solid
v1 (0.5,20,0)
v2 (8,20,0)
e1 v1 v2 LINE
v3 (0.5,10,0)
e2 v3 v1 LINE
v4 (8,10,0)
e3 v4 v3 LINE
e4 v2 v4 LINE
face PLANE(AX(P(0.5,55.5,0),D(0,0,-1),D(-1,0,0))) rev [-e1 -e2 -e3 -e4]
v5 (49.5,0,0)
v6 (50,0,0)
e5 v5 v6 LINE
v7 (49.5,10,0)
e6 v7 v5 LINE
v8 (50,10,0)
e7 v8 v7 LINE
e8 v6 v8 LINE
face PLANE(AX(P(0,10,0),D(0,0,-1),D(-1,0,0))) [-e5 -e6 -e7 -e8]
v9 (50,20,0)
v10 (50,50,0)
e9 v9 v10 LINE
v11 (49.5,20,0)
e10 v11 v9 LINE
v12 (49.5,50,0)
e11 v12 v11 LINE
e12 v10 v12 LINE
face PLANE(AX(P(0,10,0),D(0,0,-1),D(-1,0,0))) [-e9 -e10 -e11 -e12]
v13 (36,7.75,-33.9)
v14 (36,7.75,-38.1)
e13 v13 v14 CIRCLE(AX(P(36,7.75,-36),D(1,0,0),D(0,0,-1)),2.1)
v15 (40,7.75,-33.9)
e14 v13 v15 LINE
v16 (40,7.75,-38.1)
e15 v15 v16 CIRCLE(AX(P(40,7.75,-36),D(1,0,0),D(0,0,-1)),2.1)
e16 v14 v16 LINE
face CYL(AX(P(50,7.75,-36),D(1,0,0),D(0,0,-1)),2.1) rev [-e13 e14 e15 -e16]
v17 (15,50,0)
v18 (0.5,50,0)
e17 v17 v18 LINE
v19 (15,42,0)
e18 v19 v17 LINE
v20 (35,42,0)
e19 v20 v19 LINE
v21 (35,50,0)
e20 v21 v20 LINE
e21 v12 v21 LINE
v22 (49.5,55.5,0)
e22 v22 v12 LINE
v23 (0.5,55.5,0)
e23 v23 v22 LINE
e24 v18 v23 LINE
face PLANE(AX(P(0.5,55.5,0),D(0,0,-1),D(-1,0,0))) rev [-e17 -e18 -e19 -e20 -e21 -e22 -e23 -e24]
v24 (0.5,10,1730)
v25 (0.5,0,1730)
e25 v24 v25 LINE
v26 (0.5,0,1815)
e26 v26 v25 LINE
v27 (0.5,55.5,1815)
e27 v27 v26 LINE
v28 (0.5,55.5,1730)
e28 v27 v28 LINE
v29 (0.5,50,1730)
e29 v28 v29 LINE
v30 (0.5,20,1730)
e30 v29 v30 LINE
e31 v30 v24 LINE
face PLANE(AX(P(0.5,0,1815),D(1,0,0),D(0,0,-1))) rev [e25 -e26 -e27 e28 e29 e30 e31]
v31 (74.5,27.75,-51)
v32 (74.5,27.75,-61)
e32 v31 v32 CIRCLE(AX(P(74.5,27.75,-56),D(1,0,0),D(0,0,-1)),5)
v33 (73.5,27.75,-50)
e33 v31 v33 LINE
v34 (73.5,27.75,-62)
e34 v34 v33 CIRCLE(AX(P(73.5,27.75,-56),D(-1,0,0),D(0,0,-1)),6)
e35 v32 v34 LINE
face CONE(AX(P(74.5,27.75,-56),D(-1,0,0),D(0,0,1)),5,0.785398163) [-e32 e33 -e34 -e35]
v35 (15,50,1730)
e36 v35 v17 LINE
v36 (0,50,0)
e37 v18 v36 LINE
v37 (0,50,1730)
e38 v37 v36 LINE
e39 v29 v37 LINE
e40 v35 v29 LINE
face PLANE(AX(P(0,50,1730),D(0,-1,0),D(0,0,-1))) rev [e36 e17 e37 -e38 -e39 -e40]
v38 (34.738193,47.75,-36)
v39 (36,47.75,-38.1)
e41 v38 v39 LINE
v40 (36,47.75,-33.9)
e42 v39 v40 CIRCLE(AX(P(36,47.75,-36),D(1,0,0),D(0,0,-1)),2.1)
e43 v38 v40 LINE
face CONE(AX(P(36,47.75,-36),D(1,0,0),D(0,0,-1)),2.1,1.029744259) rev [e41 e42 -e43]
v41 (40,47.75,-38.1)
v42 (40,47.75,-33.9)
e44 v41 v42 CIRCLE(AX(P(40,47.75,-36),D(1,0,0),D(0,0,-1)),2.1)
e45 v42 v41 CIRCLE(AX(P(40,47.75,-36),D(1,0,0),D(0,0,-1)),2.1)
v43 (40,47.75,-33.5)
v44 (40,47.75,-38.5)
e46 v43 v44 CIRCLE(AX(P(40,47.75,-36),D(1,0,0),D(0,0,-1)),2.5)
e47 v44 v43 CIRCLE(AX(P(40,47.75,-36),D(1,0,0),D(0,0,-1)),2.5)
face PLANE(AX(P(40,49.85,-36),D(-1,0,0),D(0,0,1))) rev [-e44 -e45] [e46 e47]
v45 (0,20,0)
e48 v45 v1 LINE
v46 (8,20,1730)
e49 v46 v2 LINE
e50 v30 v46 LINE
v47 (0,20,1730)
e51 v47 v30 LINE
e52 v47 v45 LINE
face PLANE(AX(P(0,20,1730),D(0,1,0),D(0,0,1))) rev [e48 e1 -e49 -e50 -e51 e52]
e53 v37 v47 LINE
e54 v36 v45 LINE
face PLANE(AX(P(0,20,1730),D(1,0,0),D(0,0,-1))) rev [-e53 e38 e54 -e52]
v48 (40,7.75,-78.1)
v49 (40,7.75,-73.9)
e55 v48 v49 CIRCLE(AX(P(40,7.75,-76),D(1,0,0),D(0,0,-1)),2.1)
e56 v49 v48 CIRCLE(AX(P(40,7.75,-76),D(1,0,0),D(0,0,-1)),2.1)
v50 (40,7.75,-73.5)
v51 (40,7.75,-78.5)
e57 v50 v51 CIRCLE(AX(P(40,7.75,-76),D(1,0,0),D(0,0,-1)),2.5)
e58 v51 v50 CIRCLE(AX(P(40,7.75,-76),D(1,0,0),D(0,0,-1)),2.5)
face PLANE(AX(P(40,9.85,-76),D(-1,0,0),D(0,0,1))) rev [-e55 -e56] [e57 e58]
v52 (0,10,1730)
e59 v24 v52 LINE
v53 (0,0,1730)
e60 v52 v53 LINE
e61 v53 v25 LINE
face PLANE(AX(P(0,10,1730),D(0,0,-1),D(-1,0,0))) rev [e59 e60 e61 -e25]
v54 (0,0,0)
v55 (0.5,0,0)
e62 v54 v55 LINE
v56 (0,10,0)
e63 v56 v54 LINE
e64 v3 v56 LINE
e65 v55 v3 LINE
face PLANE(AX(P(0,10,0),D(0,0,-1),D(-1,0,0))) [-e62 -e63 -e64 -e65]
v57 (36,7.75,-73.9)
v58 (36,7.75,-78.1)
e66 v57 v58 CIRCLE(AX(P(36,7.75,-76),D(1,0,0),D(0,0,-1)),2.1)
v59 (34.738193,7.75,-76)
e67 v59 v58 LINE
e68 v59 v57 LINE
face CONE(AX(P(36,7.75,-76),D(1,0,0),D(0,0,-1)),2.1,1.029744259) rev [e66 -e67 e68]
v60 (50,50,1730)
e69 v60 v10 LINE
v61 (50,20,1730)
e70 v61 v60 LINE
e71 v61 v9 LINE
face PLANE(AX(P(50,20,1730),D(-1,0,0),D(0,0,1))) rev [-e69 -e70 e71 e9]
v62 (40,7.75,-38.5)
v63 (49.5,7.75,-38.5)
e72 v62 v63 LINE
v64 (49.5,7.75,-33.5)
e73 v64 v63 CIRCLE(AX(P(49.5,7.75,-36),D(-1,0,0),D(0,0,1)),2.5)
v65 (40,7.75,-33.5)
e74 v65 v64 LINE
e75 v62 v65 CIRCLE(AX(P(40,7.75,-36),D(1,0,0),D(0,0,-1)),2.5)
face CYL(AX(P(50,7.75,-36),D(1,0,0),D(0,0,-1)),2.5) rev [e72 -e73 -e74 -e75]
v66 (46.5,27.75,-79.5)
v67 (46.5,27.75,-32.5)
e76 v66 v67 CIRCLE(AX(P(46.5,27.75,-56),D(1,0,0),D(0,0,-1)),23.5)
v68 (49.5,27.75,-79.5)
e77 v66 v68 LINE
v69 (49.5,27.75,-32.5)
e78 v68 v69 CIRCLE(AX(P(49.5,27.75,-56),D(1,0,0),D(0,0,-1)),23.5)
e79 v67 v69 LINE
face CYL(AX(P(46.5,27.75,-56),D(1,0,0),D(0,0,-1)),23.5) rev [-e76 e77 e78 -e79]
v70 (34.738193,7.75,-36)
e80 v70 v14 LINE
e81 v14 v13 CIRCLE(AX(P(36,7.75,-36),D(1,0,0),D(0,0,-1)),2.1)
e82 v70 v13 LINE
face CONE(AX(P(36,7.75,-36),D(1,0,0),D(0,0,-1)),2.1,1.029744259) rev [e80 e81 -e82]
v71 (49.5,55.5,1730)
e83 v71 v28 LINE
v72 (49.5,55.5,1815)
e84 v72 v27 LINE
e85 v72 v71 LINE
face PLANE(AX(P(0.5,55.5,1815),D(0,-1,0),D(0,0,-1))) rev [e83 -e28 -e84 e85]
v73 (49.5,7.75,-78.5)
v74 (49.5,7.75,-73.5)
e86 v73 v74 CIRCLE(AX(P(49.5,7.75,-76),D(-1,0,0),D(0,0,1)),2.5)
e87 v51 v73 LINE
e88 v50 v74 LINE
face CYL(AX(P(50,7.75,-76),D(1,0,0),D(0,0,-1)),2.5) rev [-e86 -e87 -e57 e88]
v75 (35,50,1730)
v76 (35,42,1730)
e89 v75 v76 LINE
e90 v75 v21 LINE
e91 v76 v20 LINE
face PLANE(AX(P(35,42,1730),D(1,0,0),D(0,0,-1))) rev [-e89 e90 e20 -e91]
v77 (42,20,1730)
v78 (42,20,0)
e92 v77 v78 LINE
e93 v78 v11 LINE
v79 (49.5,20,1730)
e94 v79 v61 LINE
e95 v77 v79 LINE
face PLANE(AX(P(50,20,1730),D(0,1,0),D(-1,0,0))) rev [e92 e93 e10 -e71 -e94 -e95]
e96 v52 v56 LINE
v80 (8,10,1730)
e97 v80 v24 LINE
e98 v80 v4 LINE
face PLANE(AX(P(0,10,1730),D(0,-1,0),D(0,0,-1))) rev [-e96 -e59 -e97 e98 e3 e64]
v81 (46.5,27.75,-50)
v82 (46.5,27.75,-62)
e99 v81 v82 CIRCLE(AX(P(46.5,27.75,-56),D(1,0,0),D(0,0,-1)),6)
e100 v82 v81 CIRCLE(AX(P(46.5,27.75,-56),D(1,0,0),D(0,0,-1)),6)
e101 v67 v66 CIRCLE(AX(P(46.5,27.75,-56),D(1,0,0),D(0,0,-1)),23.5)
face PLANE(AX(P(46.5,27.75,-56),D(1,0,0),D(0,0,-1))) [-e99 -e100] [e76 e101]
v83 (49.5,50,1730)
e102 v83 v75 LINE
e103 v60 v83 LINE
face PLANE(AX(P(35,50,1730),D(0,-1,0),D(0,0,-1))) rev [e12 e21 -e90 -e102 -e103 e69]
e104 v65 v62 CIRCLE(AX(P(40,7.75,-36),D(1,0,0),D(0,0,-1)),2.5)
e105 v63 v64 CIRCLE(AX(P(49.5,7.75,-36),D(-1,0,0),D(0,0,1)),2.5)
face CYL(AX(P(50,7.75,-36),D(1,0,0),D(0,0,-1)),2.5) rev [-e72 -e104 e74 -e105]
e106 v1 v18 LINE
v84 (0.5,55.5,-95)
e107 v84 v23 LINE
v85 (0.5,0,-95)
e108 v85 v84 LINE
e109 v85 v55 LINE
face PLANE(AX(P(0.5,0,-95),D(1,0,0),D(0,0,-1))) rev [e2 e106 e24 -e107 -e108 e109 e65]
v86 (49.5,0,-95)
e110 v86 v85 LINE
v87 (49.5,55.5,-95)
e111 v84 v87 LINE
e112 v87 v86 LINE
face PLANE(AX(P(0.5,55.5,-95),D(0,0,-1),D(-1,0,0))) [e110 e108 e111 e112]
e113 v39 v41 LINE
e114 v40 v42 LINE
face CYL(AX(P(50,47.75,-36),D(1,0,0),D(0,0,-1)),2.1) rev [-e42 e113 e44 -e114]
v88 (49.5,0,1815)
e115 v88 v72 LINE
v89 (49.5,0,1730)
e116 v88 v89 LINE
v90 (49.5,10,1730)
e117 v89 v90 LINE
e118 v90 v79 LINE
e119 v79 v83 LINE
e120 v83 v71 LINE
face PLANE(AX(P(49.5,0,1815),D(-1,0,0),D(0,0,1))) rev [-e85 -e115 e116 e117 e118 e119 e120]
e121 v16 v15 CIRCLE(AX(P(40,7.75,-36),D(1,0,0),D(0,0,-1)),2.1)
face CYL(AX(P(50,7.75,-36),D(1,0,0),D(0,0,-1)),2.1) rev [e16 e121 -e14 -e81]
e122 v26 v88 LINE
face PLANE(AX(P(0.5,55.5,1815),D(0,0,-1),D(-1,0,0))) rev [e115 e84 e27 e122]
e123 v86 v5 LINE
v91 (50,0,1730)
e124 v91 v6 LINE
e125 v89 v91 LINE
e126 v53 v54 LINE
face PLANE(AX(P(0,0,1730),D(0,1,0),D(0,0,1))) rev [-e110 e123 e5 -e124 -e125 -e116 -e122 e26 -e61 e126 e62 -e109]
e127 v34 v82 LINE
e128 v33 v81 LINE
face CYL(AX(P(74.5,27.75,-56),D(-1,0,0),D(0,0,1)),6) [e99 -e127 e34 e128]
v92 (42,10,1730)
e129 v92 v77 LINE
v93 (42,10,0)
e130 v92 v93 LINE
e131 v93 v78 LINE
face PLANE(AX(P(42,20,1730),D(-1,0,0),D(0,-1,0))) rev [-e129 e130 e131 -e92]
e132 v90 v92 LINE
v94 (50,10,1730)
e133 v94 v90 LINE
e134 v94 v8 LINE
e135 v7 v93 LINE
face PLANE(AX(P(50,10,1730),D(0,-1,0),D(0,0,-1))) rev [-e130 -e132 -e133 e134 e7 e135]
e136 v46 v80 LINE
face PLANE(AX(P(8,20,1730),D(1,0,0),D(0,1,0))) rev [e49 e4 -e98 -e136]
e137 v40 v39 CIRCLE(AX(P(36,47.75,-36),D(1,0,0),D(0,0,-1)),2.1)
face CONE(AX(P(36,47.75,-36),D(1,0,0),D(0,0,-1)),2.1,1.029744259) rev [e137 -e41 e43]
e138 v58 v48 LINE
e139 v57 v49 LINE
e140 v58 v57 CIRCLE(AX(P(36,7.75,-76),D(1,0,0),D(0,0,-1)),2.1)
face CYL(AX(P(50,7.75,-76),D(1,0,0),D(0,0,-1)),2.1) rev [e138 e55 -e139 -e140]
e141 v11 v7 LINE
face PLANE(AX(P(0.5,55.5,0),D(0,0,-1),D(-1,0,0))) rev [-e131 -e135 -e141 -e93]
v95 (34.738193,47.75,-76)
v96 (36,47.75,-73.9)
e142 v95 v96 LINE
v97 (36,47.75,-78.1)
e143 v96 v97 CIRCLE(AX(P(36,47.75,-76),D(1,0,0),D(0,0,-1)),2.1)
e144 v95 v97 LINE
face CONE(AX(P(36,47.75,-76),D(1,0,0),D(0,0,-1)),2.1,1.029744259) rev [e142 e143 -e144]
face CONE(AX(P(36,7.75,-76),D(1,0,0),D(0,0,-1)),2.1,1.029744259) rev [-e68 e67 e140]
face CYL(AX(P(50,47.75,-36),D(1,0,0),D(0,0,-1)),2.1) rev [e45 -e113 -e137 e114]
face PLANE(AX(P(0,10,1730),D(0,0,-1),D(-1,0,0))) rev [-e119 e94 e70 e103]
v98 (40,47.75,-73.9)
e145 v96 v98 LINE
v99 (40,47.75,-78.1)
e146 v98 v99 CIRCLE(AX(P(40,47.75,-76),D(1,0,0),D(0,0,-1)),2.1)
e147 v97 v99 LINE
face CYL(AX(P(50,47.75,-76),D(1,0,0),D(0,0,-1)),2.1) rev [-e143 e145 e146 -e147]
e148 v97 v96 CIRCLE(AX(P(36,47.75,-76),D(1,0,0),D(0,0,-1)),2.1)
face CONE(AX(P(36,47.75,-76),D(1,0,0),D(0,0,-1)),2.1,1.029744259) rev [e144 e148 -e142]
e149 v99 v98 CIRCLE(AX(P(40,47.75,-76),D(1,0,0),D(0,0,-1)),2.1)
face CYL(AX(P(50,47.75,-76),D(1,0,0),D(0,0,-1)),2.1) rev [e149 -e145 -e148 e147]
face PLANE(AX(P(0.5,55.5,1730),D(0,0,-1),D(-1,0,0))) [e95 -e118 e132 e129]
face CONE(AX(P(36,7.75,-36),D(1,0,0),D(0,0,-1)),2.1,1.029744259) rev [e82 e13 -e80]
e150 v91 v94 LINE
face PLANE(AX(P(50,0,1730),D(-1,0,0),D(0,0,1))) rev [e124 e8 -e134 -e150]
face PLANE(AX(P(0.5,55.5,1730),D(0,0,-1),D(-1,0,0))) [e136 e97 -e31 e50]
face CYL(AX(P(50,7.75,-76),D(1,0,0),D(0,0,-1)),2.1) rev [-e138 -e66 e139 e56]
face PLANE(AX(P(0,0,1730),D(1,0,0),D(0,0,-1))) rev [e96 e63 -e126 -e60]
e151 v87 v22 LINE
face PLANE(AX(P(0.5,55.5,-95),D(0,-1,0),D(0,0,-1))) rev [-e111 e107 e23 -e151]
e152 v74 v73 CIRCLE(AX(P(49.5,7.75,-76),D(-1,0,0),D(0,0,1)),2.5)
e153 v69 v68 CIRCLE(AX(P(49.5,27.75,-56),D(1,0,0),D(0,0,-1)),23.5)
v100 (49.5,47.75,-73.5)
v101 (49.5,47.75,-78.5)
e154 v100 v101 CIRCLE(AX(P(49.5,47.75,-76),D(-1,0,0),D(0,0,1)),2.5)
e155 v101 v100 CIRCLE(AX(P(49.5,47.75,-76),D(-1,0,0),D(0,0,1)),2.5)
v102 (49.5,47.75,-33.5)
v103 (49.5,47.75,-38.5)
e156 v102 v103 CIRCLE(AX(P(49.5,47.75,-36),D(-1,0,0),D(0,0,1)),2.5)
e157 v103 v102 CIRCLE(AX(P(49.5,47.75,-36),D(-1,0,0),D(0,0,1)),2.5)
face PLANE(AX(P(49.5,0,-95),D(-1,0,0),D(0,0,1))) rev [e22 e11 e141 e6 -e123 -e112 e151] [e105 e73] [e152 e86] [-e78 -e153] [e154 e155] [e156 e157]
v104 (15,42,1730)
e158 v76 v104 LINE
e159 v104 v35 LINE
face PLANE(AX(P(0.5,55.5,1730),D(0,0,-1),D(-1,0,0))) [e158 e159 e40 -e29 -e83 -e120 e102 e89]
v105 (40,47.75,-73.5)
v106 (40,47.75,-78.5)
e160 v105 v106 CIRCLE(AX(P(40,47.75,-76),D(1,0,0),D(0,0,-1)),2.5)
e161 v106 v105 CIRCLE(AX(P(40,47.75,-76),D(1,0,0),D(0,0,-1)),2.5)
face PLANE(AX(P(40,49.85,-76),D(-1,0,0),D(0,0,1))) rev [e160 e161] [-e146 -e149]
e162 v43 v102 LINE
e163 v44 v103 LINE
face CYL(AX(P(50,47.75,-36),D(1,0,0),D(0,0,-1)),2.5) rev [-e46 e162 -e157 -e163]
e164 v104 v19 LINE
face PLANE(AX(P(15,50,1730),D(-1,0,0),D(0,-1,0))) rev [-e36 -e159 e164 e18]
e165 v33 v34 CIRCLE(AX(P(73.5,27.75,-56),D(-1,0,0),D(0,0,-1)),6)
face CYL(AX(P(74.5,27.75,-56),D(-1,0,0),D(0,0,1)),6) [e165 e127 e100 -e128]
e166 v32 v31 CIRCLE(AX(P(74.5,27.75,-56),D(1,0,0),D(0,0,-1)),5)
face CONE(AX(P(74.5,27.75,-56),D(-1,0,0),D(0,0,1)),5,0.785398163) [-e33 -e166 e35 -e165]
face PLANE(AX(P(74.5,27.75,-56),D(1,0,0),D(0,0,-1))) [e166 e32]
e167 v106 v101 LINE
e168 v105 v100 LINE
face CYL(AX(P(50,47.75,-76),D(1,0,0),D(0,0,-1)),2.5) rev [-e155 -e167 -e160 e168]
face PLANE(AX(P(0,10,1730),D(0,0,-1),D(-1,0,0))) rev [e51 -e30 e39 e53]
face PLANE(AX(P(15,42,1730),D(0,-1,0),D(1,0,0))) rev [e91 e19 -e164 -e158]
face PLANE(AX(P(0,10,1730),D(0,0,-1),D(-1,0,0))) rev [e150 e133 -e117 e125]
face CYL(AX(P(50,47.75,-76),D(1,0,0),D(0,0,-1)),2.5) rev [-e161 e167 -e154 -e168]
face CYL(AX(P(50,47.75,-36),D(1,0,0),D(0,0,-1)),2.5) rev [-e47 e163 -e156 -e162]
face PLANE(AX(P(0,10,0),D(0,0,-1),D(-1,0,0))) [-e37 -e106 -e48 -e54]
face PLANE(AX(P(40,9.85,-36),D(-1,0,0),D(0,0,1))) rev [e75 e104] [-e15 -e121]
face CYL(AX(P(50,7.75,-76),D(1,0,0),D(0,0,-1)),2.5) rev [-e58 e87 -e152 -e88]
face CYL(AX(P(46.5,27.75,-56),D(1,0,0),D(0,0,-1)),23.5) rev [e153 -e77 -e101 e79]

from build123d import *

# Parameters (mm, degrees)
EXTRUDE_670_DEPTH        = 1730
SKETCH_2_W               = 49
SKETCH_2_H               = 55.5
EXTRUDE_1_DEPTH          = 85
SKETCH_4_W               = 49
SKETCH_4_H               = 55.5
EXTRUDE_3_DEPTH          = 95
SKETCH_9_R               = 23.5
CUT_EXTRUDE_5_DEPTH      = 3
SKETCH_10_R              = 6
EXTRUDE_4_DEPTH          = 28
CHAMFER_1_SIZE           = 1
PATTERN_CIRCULAR_1_COUNT = 4


with BuildPart() as part:
    # 草图1 → Extrude 670 (new body)
    with BuildSketch(Plane.XY):
        Polygon((15, 50), (15, 42), (35, 42), (35, 50), (50, 50), (50, 20), (42, 20), (42, 10), (50, 10), (50, 0), (0, 0), (0, 10), (8, 10), (8, 20), (0, 20), (0, 50), align=None)
    extrude(amount=EXTRUDE_670_DEPTH)

    # 草图2 → 凸台-拉伸1 (add)
    with BuildSketch(Plane.XY.offset(1730)):
        with Locations((25, 27.75)):
            Rectangle(SKETCH_2_W, SKETCH_2_H)
    extrude(amount=EXTRUDE_1_DEPTH)

    # 草图4 → 凸台-拉伸3 (add)
    with BuildSketch(Plane(origin=(0, 0, 0), x_dir=(-1, 0, 0), z_dir=(0, 0, -1))):
        with Locations((-25, 27.75)):
            Rectangle(SKETCH_4_W, SKETCH_4_H)
    extrude(amount=EXTRUDE_3_DEPTH)

    # 草图9 → 切除-拉伸5 (cut)
    with BuildSketch(Plane(origin=(49.5, 0, 0), x_dir=(0, 0, -1), z_dir=(1, 0, 0))):
        with Locations((56, 27.75)):
            Circle(SKETCH_9_R)
    extrude(amount=-CUT_EXTRUDE_5_DEPTH, mode=Mode.SUBTRACT)

    # 草图10 → 凸台-拉伸4 (add)
    with BuildSketch(Plane(origin=(46.5, 0, 0), x_dir=(0, 0, -1), z_dir=(1, 0, 0))):
        with Locations((56, 27.75)):
            Circle(SKETCH_10_R)
    extrude(amount=EXTRUDE_4_DEPTH)

    # 倒角1
    chamfer_1_edges = [part.edges().sort_by_distance(p)[0] for p in [
        (74.5, 27.75, -50),
    ]]
    chamfer(chamfer_1_edges, length=CHAMFER_1_SIZE)

    # 草图12 → M5 螺纹孔1 (revolve, cut)
    with BuildSketch(Plane(origin=(50, 47.75, -76), x_dir=(0, 0, -1), z_dir=(0, 1, 0))):
        Polygon((0, 0), (0, 15.2618073), (2.1, 14), (2.1, 10), (2.5, 10), (2.5, 0), align=None)
    hole_wizard_m5_1 = revolve(axis=Axis((56.35, 47.75, -76), (-1, 0, 0)), mode=Mode.SUBTRACT)

    # 阵列(圆周)1: M5 螺纹孔1 ×4 about axis
    pattern_circular_1_axis = Axis((0, 27.75, -56), (1, 0, 0))
    for i in range(1, PATTERN_CIRCULAR_1_COUNT):
        add(hole_wizard_m5_1.rotate(pattern_circular_1_axis, i * 360 / PATTERN_CIRCULAR_1_COUNT), mode=Mode.SUBTRACT)


solid = part.part
